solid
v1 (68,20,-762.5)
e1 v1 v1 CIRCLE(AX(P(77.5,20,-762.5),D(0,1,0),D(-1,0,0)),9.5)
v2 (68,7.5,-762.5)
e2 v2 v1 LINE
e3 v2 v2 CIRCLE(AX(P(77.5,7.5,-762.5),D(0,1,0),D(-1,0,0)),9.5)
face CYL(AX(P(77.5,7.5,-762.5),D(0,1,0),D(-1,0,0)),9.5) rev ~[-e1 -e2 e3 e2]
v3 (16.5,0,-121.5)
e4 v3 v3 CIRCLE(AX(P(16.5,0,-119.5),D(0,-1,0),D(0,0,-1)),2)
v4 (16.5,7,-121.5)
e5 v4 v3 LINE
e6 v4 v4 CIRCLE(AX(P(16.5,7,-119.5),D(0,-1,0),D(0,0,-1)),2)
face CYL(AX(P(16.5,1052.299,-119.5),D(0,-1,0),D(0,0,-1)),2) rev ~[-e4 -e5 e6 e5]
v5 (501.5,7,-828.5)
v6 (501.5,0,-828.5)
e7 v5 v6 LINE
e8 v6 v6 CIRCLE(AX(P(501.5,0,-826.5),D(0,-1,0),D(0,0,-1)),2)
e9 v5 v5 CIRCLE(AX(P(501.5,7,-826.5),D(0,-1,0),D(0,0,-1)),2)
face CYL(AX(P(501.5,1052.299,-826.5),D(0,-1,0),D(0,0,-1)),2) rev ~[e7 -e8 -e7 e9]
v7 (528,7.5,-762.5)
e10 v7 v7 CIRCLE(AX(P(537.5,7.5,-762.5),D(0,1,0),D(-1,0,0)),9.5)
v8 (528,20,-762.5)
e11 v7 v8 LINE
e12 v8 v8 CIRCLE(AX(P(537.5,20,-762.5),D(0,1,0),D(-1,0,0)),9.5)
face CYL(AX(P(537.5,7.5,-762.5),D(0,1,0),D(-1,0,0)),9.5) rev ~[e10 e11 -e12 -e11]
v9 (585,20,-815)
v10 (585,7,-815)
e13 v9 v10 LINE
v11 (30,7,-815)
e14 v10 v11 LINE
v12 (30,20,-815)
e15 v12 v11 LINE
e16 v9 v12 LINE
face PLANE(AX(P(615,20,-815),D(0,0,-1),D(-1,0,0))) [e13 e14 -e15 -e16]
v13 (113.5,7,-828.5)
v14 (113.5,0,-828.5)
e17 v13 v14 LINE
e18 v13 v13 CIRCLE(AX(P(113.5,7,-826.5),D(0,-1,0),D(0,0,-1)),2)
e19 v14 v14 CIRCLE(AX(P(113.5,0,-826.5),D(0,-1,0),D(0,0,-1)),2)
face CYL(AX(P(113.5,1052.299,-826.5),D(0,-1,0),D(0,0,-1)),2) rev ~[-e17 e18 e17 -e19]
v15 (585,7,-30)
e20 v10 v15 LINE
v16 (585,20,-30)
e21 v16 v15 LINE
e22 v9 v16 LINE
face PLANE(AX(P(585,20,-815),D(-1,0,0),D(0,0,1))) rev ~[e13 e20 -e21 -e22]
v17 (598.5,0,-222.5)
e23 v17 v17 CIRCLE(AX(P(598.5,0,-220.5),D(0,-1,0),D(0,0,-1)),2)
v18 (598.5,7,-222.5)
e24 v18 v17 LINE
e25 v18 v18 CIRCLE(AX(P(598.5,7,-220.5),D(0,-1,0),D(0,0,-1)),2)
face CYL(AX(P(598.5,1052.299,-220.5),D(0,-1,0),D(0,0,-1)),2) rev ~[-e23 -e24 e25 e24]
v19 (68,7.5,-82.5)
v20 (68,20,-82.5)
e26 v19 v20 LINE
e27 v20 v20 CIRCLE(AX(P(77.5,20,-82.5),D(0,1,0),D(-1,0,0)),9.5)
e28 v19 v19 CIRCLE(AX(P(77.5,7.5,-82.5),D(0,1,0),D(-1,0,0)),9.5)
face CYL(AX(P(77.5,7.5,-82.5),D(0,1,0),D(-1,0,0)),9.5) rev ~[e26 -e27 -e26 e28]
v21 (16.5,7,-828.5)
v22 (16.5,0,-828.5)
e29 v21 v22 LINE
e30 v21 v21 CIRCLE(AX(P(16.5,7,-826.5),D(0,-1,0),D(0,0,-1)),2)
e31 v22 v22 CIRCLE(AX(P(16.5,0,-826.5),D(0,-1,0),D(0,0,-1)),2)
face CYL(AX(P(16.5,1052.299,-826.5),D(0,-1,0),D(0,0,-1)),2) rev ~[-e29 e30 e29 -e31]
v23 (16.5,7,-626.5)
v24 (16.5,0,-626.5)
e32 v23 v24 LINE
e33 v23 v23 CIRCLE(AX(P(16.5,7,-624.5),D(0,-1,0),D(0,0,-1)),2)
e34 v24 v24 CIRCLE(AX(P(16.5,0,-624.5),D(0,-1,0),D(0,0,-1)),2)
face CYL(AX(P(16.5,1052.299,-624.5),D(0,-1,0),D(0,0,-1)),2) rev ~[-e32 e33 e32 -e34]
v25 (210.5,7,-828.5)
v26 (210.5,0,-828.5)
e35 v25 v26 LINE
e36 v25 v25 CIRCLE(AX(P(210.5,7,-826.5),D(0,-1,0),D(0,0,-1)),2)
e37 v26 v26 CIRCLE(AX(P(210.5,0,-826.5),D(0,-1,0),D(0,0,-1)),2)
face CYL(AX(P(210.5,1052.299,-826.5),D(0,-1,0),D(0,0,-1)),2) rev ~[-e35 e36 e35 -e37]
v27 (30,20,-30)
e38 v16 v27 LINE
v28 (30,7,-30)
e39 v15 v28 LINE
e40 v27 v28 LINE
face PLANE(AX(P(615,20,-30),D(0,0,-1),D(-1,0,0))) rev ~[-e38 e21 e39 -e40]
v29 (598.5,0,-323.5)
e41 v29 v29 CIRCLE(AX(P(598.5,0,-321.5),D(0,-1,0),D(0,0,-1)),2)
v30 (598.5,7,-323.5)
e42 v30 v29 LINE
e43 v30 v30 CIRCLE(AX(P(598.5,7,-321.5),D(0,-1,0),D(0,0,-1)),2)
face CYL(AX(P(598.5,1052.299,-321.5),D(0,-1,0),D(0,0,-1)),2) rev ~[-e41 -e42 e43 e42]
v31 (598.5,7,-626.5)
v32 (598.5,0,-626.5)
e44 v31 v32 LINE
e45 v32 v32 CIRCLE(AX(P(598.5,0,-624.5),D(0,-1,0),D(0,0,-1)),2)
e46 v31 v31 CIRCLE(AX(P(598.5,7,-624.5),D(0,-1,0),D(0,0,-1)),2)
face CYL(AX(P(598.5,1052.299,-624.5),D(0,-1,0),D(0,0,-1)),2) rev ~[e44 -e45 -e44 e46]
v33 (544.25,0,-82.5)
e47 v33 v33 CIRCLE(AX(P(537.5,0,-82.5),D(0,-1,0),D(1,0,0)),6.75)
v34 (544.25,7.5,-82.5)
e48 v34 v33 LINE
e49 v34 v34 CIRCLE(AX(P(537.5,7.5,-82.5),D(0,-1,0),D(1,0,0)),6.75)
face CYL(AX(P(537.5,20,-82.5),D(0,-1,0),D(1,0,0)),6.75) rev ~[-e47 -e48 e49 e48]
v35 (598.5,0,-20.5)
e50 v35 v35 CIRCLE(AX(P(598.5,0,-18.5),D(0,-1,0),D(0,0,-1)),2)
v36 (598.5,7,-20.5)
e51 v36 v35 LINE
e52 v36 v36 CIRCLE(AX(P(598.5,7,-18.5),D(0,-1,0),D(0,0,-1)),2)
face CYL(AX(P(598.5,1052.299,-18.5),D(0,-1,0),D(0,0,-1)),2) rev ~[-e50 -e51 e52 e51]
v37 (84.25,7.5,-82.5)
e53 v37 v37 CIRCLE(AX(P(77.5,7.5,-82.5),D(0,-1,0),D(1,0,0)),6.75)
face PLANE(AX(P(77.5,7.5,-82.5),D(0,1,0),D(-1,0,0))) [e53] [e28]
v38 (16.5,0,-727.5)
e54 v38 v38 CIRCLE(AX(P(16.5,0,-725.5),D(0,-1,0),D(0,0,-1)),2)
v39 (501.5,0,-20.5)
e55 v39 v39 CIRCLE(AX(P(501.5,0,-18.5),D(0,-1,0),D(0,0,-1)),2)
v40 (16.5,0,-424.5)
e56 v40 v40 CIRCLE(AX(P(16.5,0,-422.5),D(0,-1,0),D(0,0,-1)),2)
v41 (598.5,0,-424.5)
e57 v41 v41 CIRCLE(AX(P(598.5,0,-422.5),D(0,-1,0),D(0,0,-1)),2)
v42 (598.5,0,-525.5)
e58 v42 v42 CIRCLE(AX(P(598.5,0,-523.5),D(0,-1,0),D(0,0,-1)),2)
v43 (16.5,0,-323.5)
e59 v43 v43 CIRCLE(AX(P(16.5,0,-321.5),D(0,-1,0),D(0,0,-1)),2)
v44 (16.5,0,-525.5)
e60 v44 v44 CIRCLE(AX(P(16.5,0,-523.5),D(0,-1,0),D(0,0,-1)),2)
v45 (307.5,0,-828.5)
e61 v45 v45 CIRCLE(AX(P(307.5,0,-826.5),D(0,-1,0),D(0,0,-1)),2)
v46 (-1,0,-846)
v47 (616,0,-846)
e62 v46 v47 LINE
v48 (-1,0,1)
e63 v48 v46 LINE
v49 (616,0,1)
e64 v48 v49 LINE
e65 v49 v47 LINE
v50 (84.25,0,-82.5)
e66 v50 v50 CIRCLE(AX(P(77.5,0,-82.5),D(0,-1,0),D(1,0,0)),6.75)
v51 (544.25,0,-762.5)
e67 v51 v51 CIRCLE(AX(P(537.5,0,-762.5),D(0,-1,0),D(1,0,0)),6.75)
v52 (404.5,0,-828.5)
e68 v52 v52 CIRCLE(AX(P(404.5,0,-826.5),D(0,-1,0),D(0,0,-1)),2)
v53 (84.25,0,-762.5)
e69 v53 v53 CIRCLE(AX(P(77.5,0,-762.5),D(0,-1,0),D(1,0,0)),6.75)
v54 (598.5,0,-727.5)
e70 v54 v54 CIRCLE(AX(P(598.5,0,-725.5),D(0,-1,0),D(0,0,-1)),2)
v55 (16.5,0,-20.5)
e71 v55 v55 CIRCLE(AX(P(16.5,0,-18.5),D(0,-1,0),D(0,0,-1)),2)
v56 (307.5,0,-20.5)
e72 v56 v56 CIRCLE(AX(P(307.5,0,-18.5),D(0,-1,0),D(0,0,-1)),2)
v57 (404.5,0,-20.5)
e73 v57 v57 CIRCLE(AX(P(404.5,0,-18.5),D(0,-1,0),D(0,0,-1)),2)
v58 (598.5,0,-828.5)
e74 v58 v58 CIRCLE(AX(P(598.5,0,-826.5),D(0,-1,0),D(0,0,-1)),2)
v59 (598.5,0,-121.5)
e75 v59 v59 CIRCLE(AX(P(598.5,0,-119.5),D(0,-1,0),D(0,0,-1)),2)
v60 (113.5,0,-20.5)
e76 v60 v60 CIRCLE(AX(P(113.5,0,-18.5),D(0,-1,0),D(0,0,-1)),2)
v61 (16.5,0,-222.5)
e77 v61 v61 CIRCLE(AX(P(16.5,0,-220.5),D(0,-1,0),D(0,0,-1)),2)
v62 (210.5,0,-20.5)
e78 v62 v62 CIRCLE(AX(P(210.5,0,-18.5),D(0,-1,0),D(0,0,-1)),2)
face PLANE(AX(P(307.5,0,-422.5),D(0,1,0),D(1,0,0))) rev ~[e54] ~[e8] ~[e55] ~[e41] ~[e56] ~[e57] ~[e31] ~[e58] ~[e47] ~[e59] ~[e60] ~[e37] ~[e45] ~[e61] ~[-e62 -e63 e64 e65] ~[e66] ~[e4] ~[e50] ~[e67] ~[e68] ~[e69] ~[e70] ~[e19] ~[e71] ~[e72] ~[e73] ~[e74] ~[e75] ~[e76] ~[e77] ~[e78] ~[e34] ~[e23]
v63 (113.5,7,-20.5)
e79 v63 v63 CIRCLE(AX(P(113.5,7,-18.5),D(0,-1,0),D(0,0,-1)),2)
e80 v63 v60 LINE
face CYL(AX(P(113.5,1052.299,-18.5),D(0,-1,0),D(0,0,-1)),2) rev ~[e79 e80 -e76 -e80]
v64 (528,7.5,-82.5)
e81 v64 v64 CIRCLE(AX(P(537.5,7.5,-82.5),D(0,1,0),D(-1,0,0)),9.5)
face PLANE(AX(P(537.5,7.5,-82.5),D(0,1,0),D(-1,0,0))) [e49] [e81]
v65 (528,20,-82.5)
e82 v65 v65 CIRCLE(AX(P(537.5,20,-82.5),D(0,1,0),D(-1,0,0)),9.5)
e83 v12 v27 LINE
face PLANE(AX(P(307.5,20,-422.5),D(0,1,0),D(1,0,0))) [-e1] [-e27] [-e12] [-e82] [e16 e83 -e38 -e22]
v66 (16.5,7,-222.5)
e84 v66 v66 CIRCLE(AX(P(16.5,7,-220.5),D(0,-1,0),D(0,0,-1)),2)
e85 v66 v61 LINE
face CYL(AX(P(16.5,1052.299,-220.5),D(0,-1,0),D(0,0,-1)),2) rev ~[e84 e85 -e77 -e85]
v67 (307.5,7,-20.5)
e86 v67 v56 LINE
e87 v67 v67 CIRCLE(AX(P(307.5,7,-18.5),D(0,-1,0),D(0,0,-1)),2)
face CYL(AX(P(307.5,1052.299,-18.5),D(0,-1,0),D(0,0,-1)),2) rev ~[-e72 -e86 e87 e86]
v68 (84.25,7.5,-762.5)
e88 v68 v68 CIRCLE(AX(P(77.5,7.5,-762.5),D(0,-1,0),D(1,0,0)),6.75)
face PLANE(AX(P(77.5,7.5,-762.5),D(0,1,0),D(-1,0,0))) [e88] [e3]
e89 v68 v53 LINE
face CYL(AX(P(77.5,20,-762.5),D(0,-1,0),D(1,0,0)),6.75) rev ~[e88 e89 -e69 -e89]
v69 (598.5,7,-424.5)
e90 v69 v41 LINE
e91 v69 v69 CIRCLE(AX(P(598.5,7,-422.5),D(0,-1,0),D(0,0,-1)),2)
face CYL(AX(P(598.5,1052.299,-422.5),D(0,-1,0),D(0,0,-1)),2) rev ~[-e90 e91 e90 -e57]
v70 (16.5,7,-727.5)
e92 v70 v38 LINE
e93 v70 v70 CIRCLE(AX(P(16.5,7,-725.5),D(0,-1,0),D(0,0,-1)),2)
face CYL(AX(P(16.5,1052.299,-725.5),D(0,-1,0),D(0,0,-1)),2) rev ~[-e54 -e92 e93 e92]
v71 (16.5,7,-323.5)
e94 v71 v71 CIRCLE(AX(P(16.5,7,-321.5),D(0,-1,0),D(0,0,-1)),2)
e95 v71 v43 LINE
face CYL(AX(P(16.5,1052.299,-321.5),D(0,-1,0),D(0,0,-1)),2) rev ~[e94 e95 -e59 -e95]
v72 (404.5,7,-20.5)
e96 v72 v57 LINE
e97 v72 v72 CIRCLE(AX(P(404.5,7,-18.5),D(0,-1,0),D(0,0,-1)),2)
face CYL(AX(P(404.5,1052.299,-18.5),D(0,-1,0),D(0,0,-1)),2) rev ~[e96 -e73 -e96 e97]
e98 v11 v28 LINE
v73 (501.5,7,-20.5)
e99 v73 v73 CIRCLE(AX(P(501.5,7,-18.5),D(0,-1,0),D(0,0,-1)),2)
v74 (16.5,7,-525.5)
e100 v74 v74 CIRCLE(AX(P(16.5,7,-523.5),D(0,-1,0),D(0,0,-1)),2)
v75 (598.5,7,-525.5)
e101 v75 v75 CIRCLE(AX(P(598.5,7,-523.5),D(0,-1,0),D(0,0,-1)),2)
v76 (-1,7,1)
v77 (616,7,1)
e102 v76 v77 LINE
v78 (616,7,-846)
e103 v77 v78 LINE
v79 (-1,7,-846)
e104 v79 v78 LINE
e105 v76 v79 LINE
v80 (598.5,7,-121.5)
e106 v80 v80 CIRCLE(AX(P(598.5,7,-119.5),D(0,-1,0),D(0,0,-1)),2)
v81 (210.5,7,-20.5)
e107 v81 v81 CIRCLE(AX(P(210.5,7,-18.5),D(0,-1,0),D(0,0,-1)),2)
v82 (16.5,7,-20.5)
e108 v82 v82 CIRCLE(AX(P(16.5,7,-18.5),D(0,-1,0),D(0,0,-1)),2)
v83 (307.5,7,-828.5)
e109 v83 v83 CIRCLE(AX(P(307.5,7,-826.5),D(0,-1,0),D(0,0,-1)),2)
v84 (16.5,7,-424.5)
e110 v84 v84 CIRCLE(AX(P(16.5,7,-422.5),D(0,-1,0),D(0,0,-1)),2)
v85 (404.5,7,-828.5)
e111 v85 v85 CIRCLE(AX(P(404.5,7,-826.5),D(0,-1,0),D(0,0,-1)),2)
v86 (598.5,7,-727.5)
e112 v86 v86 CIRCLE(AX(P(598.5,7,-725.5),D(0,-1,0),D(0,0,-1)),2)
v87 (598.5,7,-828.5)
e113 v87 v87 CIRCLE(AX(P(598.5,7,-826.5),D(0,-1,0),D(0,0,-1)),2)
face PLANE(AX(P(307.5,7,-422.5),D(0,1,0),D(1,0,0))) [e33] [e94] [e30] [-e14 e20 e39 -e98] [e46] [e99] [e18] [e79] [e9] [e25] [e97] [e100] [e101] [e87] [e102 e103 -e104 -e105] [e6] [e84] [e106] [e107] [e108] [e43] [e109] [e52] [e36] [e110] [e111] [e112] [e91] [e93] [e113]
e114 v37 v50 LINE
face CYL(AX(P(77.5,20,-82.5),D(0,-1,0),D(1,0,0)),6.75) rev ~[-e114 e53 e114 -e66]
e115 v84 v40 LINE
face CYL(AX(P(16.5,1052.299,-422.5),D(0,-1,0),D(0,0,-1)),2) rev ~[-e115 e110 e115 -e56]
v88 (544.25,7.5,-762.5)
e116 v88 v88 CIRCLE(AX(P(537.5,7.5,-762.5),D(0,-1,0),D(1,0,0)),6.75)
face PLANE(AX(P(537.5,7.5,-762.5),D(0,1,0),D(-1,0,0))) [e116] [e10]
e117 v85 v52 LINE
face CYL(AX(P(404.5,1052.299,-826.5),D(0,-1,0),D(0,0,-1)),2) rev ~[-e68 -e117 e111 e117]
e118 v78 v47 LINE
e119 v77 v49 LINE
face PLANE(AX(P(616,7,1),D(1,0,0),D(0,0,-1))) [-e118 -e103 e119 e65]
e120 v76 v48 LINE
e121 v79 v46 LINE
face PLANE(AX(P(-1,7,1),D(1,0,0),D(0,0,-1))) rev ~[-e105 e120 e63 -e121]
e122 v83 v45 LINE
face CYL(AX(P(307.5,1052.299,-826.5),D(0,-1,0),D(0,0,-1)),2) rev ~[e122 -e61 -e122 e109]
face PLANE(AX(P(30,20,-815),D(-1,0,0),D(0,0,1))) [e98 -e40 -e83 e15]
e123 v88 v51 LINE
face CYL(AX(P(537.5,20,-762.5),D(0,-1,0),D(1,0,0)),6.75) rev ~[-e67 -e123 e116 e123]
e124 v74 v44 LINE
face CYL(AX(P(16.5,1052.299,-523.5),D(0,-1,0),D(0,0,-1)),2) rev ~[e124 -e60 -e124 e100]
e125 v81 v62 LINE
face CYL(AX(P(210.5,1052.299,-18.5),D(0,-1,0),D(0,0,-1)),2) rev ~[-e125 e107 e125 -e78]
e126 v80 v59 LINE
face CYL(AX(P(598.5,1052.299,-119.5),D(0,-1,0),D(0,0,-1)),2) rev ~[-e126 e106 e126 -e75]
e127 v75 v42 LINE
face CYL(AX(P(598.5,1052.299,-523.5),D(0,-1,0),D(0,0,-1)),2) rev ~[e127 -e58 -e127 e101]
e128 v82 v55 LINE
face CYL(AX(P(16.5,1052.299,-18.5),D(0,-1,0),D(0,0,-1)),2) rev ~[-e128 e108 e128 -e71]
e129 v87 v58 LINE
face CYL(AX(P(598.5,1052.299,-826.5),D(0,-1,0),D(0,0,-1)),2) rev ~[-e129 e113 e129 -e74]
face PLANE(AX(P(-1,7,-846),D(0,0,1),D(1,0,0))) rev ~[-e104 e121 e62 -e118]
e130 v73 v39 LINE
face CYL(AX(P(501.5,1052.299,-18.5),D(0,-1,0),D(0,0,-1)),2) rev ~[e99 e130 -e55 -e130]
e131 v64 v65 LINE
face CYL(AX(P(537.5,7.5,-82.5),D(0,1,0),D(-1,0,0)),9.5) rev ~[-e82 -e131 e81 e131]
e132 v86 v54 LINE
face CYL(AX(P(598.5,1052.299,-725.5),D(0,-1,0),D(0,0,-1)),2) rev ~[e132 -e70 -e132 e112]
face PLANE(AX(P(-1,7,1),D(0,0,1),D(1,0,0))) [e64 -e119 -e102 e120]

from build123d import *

# Parameters (mm, degrees)
SKETCH_1_W                    = 615
SKETCH_1_H                    = 845
EXTRUDE_1_DEPTH               = 20
SKETCH_2_W                    = 615
SKETCH_2_H                    = 30
CUT_EXTRUDE_1_DEPTH           = 13
SKETCH_3_W                    = 30
SKETCH_3_H                    = 785
CUT_EXTRUDE_2_DEPTH           = 13
HOLE_WIZARD_M4_1_D            = 4
PATTERN_LINEAR_3_COUNT        = 8
PATTERN_LINEAR_3_PITCH        = 101
PATTERN_LINEAR_4_COUNT        = 6
PATTERN_LINEAR_4_PITCH        = 97
SKETCH_15_W                   = 617
SKETCH_15_H                   = 847
SKETCH_15_W_2                 = 615
SKETCH_15_H_2                 = 845
EXTRUDE_5_DEPTH               = 7
SKETCH_17_R                   = 2.5
CUT_EXTRUDE_3_DEPTH           = 20
HOLE_WIZARD_M12_2_D           = 13.5
HOLE_WIZARD_M12_2_CBORE_D     = 19
HOLE_WIZARD_M12_2_CBORE_DEPTH = 12.5
PATTERN_LINEAR_7_COUNT        = 2
PATTERN_LINEAR_7_PITCH        = 680


with BuildPart() as part:
    # 草图1 → 拉伸1 (new body)
    with BuildSketch(Plane(origin=(0, 0, 0), x_dir=(1, 0, 0), z_dir=(0, 1, 0))):
        with Locations((307.5, 422.5)):
            Rectangle(SKETCH_1_W, SKETCH_1_H)
    extrude(amount=EXTRUDE_1_DEPTH)

    # 草图2 → 切除-拉伸1 (cut)
    with BuildSketch(Plane(origin=(0, 20, 0), x_dir=(-1, 0, 0), z_dir=(0, 1, 0))):
        with Locations((-307.5, -830)):
            Rectangle(SKETCH_2_W, SKETCH_2_H)
        with Locations((-307.5, -15)):
            Rectangle(SKETCH_2_W, SKETCH_2_H)
    extrude(amount=-CUT_EXTRUDE_1_DEPTH, mode=Mode.SUBTRACT)

    # 草图3 → 切除-拉伸2 (cut)
    with BuildSketch(Plane(origin=(0, 20, 0), x_dir=(-1, 0, 0), z_dir=(0, 1, 0))):
        with Locations((-600, -422.5)):
            Rectangle(SKETCH_3_W, SKETCH_3_H)
        with Locations((-15, -422.5)):
            Rectangle(SKETCH_3_W, SKETCH_3_H)
    extrude(amount=-CUT_EXTRUDE_2_DEPTH, mode=Mode.SUBTRACT)

    # M4 螺纹孔1 (through all)
    with Locations(Plane(origin=(598.5, 7, -826.5), x_dir=(0, 0, 1), z_dir=(0, 1, 0))):
        with Locations((0, 0), (0, -582), (808, -582), (808, 0)):
            hole_wizard_m4_1 = Hole(HOLE_WIZARD_M4_1_D / 2)

    # 阵列(线性)3: M4 螺纹孔1 ×8
    with Locations(*[(0, 0, i * PATTERN_LINEAR_3_PITCH) for i in range(1, PATTERN_LINEAR_3_COUNT)]):
        add(hole_wizard_m4_1, mode=Mode.SUBTRACT)

    # 阵列(线性)4: M4 螺纹孔1 ×6
    with Locations(*[(-i * PATTERN_LINEAR_4_PITCH, 0, 0) for i in range(1, PATTERN_LINEAR_4_COUNT)]):
        add(hole_wizard_m4_1, mode=Mode.SUBTRACT)

    # 草图15 → 凸台-拉伸5 (add)
    with BuildSketch(Plane(origin=(0, 7, 0), x_dir=(1, 0, 0), z_dir=(0, 1, 0))):
        with Locations((307.5, 422.5)):
            Rectangle(SKETCH_15_W, SKETCH_15_H)
        with Locations((307.5, 422.5)):
            Rectangle(SKETCH_15_W_2, SKETCH_15_H_2, mode=Mode.SUBTRACT)
    extrude(amount=-EXTRUDE_5_DEPTH)

    # 草图17 → 切除-拉伸3 (cut)
    with BuildSketch(Plane(origin=(0, 20, 0), x_dir=(1, 0, 0), z_dir=(0, 1, 0))):
        with Locations(Location((77.5, 82.5, 0), (0, 0, 270))):
            Circle(SKETCH_17_R)
        with Locations(Location((537.5, 82.5, 0), (0, 0, 270))):
            Circle(SKETCH_17_R)
    extrude(amount=-CUT_EXTRUDE_3_DEPTH, mode=Mode.SUBTRACT)

    # M12 六角头螺栓的柱形沉头孔2 (through all)
    with Locations(Plane(origin=(0, 20, 0), x_dir=(-1, 0, 0), z_dir=(0, 1, 0))):
        with Locations((-77.5, -82.5), (-537.5, -82.5)):
            hole_wizard_m12_2 = CounterBoreHole(HOLE_WIZARD_M12_2_D / 2, HOLE_WIZARD_M12_2_CBORE_D / 2, HOLE_WIZARD_M12_2_CBORE_DEPTH)

    # 阵列(线性)7: M12 六角头螺栓的柱形沉头孔2 ×2
    with Locations(*[(0, 0, -i * PATTERN_LINEAR_7_PITCH) for i in range(1, PATTERN_LINEAR_7_COUNT)]):
        add(hole_wizard_m12_2, mode=Mode.SUBTRACT)


solid = part.part
